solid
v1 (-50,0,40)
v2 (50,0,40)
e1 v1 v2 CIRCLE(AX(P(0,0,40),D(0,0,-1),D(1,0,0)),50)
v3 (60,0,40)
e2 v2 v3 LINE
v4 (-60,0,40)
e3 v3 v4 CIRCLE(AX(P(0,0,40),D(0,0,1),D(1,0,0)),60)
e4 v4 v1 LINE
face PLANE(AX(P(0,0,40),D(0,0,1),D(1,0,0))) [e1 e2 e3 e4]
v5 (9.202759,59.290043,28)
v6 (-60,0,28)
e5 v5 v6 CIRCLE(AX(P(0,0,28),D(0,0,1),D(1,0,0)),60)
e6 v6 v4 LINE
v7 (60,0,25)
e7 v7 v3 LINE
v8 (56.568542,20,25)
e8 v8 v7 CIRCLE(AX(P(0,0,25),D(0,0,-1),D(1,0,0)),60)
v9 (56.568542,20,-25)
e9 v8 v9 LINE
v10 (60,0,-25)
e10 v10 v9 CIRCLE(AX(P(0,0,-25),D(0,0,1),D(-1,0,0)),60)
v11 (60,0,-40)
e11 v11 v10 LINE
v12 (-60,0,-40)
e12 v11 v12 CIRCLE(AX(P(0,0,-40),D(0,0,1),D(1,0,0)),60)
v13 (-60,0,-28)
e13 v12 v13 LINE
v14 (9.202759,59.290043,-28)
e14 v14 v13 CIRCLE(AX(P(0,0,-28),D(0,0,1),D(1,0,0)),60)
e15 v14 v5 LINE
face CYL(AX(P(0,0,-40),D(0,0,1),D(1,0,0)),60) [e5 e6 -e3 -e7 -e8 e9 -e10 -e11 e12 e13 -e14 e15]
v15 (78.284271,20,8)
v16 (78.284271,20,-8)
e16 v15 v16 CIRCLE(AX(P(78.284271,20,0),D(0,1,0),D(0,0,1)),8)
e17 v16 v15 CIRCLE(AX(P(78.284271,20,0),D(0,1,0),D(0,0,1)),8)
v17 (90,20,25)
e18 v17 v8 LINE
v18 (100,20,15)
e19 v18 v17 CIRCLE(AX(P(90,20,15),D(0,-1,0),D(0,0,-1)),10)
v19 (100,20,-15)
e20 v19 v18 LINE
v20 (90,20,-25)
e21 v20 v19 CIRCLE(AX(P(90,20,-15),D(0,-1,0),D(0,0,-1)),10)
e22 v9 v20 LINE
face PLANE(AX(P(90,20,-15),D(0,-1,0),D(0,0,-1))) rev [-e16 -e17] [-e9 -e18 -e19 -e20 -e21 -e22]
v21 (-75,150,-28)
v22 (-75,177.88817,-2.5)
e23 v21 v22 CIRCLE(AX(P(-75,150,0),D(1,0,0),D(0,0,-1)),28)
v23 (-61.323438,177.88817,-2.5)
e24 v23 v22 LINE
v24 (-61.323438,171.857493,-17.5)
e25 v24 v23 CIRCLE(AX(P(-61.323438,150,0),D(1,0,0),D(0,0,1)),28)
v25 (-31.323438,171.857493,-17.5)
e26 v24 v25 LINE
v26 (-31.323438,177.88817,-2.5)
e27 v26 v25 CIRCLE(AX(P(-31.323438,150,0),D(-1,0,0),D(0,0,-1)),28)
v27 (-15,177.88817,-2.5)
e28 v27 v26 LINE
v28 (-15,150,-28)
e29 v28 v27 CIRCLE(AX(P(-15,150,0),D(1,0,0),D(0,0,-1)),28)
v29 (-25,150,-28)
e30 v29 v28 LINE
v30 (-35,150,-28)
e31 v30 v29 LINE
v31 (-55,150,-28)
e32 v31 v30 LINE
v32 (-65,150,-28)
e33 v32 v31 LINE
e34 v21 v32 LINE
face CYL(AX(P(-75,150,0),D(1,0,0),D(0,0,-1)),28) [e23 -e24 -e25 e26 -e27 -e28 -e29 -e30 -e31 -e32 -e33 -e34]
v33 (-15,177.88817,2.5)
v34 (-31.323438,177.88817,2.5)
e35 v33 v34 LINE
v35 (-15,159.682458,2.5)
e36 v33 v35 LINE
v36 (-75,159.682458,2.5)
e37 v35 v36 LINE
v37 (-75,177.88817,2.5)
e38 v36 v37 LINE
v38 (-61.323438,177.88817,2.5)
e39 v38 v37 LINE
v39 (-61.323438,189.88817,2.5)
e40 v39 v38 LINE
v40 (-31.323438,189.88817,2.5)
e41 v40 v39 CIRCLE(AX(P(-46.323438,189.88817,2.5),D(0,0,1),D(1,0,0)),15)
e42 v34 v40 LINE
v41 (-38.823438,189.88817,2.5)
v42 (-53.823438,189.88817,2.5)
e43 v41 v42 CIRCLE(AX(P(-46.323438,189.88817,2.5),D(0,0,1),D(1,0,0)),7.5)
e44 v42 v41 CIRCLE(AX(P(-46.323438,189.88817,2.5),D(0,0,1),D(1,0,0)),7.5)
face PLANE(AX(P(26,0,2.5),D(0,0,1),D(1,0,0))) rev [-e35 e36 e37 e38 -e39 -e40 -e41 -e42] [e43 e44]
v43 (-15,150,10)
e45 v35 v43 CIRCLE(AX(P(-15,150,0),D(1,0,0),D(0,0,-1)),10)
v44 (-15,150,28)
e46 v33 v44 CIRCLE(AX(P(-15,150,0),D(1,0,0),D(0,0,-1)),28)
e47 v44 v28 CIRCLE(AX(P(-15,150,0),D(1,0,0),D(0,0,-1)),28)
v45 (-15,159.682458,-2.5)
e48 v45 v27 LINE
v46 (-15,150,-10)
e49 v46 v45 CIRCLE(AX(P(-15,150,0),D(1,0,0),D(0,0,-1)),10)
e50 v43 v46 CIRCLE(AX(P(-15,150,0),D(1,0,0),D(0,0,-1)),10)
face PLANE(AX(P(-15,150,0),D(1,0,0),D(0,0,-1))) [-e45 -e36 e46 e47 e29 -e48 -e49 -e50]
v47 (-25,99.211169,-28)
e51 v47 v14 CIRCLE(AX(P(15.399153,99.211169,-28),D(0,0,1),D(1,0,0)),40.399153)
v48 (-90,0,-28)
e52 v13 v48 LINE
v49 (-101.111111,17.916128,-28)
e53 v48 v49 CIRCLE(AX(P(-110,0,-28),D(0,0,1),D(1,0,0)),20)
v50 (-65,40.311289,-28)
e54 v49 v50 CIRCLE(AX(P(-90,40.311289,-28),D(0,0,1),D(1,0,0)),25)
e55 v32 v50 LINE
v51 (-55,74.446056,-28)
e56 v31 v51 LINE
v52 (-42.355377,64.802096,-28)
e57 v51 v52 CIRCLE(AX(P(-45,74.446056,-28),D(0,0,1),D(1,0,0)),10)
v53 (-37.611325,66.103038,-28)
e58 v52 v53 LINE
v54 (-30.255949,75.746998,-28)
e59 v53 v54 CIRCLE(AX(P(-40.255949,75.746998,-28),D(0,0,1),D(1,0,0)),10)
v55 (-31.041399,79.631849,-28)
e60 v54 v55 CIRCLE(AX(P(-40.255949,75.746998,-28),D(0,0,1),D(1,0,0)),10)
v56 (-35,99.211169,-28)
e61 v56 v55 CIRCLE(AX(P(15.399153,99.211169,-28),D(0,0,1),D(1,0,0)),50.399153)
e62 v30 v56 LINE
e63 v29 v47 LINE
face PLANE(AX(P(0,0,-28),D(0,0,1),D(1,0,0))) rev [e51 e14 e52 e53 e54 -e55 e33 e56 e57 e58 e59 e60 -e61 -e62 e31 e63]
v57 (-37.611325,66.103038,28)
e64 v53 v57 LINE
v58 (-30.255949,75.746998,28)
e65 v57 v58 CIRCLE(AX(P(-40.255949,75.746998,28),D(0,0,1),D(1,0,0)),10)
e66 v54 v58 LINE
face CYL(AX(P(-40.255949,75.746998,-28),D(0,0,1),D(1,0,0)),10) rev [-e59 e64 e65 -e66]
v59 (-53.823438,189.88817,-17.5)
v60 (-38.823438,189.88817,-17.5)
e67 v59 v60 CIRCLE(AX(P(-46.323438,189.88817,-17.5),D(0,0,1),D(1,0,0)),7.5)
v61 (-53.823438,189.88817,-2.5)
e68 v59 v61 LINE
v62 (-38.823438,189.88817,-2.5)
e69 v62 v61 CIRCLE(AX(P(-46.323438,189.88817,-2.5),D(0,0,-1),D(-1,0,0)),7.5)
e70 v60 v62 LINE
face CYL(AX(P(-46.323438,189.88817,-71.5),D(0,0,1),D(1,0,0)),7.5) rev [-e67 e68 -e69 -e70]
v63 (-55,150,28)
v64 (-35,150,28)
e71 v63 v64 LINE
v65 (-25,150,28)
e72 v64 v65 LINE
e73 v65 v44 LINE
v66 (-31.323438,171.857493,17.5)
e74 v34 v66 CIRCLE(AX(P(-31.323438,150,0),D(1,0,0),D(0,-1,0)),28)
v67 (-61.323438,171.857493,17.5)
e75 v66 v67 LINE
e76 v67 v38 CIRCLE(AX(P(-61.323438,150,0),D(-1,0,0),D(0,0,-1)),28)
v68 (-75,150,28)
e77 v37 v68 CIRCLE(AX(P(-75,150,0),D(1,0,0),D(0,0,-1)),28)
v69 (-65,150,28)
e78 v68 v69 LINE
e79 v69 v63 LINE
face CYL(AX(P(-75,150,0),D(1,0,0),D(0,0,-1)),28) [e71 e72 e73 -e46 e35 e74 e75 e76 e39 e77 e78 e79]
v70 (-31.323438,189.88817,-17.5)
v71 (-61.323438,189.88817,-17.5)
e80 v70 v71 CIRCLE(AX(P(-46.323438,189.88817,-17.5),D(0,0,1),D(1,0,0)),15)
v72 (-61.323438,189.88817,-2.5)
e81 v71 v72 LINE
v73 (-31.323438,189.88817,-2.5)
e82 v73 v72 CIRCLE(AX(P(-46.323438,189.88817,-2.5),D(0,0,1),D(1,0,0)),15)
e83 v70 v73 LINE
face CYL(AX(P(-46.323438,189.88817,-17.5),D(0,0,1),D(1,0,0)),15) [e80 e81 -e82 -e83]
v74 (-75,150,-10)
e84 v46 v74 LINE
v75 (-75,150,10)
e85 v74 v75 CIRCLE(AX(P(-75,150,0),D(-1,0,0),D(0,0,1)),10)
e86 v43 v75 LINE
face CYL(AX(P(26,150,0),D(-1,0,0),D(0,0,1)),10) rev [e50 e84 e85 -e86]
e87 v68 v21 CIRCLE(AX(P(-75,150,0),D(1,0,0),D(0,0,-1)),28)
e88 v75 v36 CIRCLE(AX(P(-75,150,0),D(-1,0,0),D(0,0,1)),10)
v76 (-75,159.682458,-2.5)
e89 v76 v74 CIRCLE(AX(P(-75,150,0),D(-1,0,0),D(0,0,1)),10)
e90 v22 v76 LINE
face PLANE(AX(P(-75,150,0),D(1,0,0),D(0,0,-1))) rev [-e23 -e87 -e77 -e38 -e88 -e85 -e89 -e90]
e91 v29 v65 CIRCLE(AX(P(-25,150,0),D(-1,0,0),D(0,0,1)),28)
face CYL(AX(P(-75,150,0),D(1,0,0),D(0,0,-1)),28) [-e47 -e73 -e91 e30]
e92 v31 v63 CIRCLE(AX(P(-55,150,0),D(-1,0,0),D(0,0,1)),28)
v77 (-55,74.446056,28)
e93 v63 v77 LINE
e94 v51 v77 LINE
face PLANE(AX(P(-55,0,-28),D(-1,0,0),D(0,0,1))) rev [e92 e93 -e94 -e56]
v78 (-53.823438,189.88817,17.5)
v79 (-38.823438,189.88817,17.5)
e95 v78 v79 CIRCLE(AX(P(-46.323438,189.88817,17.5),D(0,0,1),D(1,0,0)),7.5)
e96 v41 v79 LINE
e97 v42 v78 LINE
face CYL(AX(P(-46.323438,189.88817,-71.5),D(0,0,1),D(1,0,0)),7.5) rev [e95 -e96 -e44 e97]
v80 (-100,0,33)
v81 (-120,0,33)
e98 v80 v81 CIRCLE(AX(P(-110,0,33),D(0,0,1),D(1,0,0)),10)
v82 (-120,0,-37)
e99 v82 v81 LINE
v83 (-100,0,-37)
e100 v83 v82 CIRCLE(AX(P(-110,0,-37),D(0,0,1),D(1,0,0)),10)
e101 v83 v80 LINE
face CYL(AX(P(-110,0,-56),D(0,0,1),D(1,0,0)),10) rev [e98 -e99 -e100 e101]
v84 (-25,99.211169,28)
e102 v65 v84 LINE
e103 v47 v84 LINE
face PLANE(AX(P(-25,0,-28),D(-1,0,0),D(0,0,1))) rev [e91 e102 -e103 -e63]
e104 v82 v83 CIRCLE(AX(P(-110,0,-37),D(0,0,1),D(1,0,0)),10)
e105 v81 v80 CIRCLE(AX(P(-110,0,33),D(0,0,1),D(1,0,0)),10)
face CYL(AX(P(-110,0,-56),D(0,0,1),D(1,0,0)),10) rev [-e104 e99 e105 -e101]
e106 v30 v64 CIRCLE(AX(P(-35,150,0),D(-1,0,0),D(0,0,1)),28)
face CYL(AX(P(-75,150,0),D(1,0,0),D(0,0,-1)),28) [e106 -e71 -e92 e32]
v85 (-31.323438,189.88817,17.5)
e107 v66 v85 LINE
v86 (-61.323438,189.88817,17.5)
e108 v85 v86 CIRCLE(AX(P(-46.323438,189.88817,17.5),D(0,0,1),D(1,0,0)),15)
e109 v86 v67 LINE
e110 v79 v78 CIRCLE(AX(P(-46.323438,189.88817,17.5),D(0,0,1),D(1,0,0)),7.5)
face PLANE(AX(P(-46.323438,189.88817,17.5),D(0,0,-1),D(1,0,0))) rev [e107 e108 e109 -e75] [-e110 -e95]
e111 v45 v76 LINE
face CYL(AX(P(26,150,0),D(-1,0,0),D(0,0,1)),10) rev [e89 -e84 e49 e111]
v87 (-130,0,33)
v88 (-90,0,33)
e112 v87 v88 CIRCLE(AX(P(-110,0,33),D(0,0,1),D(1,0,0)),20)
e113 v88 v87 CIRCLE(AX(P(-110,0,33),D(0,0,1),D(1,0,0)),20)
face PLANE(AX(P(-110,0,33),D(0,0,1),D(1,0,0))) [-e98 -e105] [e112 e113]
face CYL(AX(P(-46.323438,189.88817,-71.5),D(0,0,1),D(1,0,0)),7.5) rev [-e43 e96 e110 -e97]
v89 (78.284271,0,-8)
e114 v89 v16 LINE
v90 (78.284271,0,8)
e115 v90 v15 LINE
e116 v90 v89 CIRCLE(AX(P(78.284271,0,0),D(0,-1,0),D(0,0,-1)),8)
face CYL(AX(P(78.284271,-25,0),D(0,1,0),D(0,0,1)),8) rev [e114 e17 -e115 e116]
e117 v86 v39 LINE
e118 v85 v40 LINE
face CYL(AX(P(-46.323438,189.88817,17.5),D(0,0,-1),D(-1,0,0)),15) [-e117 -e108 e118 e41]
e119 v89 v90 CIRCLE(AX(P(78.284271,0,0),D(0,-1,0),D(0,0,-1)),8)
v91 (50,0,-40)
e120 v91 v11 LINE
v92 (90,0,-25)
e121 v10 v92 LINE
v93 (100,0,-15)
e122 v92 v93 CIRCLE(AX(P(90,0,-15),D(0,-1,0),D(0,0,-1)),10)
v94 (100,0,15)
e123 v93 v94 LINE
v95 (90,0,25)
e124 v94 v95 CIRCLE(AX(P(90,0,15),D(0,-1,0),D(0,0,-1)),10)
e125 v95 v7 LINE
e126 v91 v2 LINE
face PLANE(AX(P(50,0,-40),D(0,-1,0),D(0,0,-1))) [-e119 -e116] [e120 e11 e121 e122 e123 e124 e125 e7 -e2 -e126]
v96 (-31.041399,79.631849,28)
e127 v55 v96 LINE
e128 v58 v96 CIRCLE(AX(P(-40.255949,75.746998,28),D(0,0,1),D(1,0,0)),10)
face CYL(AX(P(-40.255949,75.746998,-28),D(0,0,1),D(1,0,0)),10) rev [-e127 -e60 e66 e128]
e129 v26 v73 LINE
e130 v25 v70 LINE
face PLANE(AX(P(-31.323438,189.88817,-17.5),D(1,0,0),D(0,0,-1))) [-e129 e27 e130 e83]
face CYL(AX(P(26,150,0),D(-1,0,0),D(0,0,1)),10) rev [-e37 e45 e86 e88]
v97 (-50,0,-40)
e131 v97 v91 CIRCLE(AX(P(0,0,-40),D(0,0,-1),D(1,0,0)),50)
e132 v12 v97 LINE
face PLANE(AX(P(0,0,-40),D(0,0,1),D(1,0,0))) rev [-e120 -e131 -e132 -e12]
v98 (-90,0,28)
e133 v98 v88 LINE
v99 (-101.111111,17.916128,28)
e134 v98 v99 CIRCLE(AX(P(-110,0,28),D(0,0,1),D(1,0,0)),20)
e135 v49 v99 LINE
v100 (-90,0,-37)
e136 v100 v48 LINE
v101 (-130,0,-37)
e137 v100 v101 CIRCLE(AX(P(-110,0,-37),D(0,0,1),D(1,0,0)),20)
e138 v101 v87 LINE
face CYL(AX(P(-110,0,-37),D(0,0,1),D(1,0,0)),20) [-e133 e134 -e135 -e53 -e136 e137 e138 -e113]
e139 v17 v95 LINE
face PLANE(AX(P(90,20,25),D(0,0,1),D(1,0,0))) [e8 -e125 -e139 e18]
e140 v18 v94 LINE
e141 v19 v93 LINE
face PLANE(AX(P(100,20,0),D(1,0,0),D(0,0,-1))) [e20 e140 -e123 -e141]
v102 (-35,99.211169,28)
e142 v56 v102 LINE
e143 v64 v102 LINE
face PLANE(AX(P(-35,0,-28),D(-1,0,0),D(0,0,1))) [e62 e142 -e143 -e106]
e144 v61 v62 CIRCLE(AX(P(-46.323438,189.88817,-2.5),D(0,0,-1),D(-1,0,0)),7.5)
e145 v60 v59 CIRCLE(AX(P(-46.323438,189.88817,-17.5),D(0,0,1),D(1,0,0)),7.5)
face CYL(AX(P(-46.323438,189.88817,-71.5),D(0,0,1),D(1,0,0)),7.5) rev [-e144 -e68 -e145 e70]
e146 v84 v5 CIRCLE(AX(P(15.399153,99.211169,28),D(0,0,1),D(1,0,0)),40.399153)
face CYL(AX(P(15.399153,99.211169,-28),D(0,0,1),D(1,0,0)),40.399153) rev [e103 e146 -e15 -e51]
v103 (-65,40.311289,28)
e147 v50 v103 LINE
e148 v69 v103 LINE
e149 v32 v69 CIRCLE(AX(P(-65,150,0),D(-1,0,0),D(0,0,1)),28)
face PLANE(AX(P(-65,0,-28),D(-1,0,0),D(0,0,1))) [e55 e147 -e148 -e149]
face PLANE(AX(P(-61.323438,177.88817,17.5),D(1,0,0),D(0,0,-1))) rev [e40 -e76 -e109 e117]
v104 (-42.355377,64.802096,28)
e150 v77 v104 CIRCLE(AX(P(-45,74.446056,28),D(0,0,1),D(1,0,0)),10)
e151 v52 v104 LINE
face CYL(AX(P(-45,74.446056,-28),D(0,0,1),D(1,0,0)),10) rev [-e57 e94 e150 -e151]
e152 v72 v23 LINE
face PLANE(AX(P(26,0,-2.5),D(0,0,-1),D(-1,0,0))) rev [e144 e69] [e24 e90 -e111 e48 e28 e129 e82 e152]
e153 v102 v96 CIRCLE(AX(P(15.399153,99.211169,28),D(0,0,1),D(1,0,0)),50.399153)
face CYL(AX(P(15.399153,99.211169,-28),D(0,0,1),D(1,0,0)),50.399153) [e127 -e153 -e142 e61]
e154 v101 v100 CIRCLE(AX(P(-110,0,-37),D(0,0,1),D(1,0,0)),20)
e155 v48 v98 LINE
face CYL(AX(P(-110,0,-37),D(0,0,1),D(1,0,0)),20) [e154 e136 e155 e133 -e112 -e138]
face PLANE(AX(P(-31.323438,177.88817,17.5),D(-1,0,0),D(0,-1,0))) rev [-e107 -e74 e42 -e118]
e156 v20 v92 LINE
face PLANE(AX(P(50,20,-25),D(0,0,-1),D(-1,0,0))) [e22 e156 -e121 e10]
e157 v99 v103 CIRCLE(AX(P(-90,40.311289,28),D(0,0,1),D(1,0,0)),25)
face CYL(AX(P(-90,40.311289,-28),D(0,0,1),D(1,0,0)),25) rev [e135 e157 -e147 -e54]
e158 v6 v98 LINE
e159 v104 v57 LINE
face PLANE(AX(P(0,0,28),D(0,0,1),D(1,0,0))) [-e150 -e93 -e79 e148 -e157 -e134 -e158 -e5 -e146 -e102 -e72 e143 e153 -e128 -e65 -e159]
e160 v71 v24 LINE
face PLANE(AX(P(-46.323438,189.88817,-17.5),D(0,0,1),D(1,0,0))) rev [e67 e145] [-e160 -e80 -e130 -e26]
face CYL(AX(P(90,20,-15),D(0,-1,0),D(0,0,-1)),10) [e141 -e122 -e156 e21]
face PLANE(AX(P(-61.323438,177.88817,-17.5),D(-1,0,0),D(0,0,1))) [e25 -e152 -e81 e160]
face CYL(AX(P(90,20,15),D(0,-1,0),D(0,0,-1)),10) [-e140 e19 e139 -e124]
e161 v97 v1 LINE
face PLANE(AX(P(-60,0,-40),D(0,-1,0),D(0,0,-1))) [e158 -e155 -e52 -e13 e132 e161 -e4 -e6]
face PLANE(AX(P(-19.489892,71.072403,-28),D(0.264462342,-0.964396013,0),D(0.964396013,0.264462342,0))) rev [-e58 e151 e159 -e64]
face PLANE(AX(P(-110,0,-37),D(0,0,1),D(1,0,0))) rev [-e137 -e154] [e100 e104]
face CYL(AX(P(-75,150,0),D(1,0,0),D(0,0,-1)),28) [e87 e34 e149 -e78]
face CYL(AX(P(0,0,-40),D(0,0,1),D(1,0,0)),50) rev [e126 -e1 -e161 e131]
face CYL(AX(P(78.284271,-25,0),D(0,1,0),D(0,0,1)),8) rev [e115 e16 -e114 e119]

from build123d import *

# Parameters (mm, degrees)
BASE_BLOCK_DEPTH             = 40
LOWER_HUB_40_DEPTH           = 5
LOWER_HUB_40_DEPTH_BACK      = 65
LOWER_HUB_40_SKETCH_R        = 20
UPPER_HUB_56_SKETCH_R        = 28
UPPER_HUB_56_DEPTH           = 60
WEB_ARM_DEPTH                = 28
SPLIT_START                  = -101
SPLIT_SLOT_DEPTH             = 101
CLAMP_EAR_DEPTH              = 15
UPPER_BORE_20_SKETCH_R       = 10
UPPER_BORE_20_DEPTH          = 89
CLAMP_SCREW_HOLE_15_SKETCH_R = 7.5
CLAMP_SCREW_HOLE_15_DEPTH    = 89
LOWER_BORE_20_SKETCH_R       = 10
LOWER_BORE_20_DEPTH          = 89
MOUNTING_FOOT_DEPTH          = 20
FOOT_HOLE_16_SKETCH_R        = 8
FOOT_HOLE_16_DEPTH           = 45


with BuildPart() as part:
    # Base Block Sketch → Base Block (new, symmetric)
    with BuildSketch(Plane.XY):
        with BuildLine():
            Line((-60, 0), (-50, 0))
            ThreePointArc((-50, 0), (0, 50), (50, 0))
            Line((50, 0), (60, 0))
            ThreePointArc((60, 0), (0, 60), (-60, 0))
        make_face()
    extrude(amount=BASE_BLOCK_DEPTH, both=True)



with BuildPart() as body_2:
    # Lower Hub Ø40 Sketch → Lower Hub Ø40 (new, two sides: drawn at the far end of the back side and taken through both)
    with BuildSketch(Plane.XY.offset(28).offset(-LOWER_HUB_40_DEPTH_BACK)):
        with Locations((-110, 0)):
            Circle(LOWER_HUB_40_SKETCH_R)
    extrude(amount=LOWER_HUB_40_DEPTH + LOWER_HUB_40_DEPTH_BACK)


with BuildPart() as body_3:
    # Upper Hub Ø56 Sketch → Upper Hub Ø56 (new body)
    with BuildSketch(Plane(origin=(-15, 0, 0), x_dir=(0, 0, -1), z_dir=(1, 0, 0))):
        with Locations((0, 150)):
            Circle(UPPER_HUB_56_SKETCH_R)
    extrude(amount=-UPPER_HUB_56_DEPTH)


with BuildPart() as part_1:
    add(part.part)

    add(body_2.part)  # Web Arm merges body 2

    add(body_3.part)  # Web Arm merges body 3
    # Web Arm Profile → Web Arm (add, symmetric)
    with BuildSketch(Plane.XY):
        with BuildLine():
            Line((-55, 74.446056073), (-55, 150))
            Line((-55, 150), (-65, 150))
            Line((-65, 150), (-65, 40.311288741))
            ThreePointArc((-65, 40.311288741), (-76.823843083, 19.065374102), (-101.111111111, 17.91612833))
            ThreePointArc((-101.111111111, 17.91612833), (-93.003268288, 10.540925534), (-90, 0))
            Line((-90, 0), (-60, 0))
            ThreePointArc((-60, 0), (-39.037382491, 45.564051271), (9.202758941, 59.290043244))
            ThreePointArc((9.202758941, 59.290043244), (-15.279998201, 72.92654907), (-25, 99.211169164))
            Line((-25, 99.211169164), (-25, 150))
            Line((-25, 150), (-35, 150))
            Line((-35, 150), (-35, 99.211169164))
            ThreePointArc((-35, 99.211169164), (-34.000437544, 89.223422766), (-31.041398663, 79.631848749))
            ThreePointArc((-31.041398663, 79.631848749), (-31.260550889, 71.378609178), (-37.611325277, 66.103037571))
            Line((-37.611325277, 66.103037571), (-42.35537658, 64.802095944))
            ThreePointArc((-42.35537658, 64.802095944), (-51.064394685, 66.494759506), (-55, 74.446056073))
        make_face()
    extrude(amount=WEB_ARM_DEPTH, both=True)

    # Split Slot Sketch → Split Slot (cut)
    with BuildSketch(Plane.ZY.offset(75).offset(SPLIT_START)):
        with BuildLine():
            Line((-2.5, 150), (0, 150))
            Line((0, 150), (2.5, 150))
            Line((2.5, 150), (2.5, 159.682458366))
            Line((2.5, 159.682458366), (2.5, 177.888169535))
            ThreePointArc((2.5, 177.888169535), (0, 178), (-2.5, 177.888169535))
            Line((-2.5, 177.888169535), (-2.5, 159.682458366))
            Line((-2.5, 159.682458366), (-2.5, 150))
        make_face()
        with BuildLine():
            Line((2.5, 150), (0, 150))
            Line((0, 150), (-2.5, 150))
            Line((-2.5, 150), (-2.5, 159.682458366))
            ThreePointArc((-2.5, 159.682458366), (0, 140), (2.5, 159.682458366))
            Line((2.5, 159.682458366), (2.5, 150))
        make_face()
    extrude(amount=SPLIT_SLOT_DEPTH, mode=Mode.SUBTRACT)

    # Clamp Ear Sketch → Clamp Ear (add)
    with BuildSketch(Plane.XY.offset(-2.5)):
        with BuildLine():
            Line((-31.323438353, 177.888169535), (-31.323438353, 149.888169535))
            Line((-31.323438353, 149.888169535), (-61.323438353, 150))
            Line((-61.323438353, 150), (-61.323438353, 177.888169535))
            Line((-61.323438353, 177.888169535), (-61.323438353, 189.888169535))
            ThreePointArc((-61.323438353, 189.888169535), (-46.323438353, 204.888169535), (-31.323438353, 189.888169535))
            Line((-31.323438353, 189.888169535), (-31.323438353, 177.888169535))
        make_face()
    clamp_ear = extrude(amount=-CLAMP_EAR_DEPTH)

    # Clamp Ear Mirror: Clamp Ear across plane
    add(clamp_ear.mirror(Plane.XY))

    # Upper Bore Ø20 Sketch → Upper Bore Ø20 (cut)
    with BuildSketch(Plane(origin=(-15, 0, 0), x_dir=(0, 0, -1), z_dir=(1, 0, 0))):
        with Locations((0, 150)):
            Circle(UPPER_BORE_20_SKETCH_R)
    extrude(amount=-UPPER_BORE_20_DEPTH, mode=Mode.SUBTRACT)

    # Clamp Screw Hole Ø15 Sketch → Clamp Screw Hole Ø15 (cut)
    with BuildSketch(Plane.XY.offset(17.5)):
        with Locations((-46.323438353, 189.888169535)):
            Circle(CLAMP_SCREW_HOLE_15_SKETCH_R)
    extrude(amount=-CLAMP_SCREW_HOLE_15_DEPTH, mode=Mode.SUBTRACT)

    # Lower Bore Ø20 Sketch → Lower Bore Ø20 (cut)
    with BuildSketch(Plane.XY.offset(33)):
        with Locations((-110, 0)):
            Circle(LOWER_BORE_20_SKETCH_R)
    extrude(amount=-LOWER_BORE_20_DEPTH, mode=Mode.SUBTRACT)

    # Mounting Foot Sketch → Mounting Foot (add)
    with BuildSketch(Plane.XZ):
        with BuildLine():
            Line((100, 0), (100, 15))
            ThreePointArc((100, 15), (97.071067812, 22.071067812), (90, 25))
            Line((90, 25), (50, 25))
            Line((50, 25), (50, -25))
            Line((50, -25), (90, -25))
            ThreePointArc((90, -25), (97.071067812, -22.071067812), (100, -15))
            Line((100, -15), (100, 0))
        make_face()
    extrude(amount=-MOUNTING_FOOT_DEPTH)

    # Foot Hole Ø16 Sketch → Foot Hole Ø16 (cut)
    with BuildSketch(Plane(origin=(0, 20, 0), x_dir=(1, 0, 0), z_dir=(0, 1, 0))):
        with Locations(Location((78.284271247, 0, 0), (0, 0, 270))):
            Circle(FOOT_HOLE_16_SKETCH_R)
    extrude(amount=-FOOT_HOLE_16_DEPTH, mode=Mode.SUBTRACT)


solid = part_1.part
